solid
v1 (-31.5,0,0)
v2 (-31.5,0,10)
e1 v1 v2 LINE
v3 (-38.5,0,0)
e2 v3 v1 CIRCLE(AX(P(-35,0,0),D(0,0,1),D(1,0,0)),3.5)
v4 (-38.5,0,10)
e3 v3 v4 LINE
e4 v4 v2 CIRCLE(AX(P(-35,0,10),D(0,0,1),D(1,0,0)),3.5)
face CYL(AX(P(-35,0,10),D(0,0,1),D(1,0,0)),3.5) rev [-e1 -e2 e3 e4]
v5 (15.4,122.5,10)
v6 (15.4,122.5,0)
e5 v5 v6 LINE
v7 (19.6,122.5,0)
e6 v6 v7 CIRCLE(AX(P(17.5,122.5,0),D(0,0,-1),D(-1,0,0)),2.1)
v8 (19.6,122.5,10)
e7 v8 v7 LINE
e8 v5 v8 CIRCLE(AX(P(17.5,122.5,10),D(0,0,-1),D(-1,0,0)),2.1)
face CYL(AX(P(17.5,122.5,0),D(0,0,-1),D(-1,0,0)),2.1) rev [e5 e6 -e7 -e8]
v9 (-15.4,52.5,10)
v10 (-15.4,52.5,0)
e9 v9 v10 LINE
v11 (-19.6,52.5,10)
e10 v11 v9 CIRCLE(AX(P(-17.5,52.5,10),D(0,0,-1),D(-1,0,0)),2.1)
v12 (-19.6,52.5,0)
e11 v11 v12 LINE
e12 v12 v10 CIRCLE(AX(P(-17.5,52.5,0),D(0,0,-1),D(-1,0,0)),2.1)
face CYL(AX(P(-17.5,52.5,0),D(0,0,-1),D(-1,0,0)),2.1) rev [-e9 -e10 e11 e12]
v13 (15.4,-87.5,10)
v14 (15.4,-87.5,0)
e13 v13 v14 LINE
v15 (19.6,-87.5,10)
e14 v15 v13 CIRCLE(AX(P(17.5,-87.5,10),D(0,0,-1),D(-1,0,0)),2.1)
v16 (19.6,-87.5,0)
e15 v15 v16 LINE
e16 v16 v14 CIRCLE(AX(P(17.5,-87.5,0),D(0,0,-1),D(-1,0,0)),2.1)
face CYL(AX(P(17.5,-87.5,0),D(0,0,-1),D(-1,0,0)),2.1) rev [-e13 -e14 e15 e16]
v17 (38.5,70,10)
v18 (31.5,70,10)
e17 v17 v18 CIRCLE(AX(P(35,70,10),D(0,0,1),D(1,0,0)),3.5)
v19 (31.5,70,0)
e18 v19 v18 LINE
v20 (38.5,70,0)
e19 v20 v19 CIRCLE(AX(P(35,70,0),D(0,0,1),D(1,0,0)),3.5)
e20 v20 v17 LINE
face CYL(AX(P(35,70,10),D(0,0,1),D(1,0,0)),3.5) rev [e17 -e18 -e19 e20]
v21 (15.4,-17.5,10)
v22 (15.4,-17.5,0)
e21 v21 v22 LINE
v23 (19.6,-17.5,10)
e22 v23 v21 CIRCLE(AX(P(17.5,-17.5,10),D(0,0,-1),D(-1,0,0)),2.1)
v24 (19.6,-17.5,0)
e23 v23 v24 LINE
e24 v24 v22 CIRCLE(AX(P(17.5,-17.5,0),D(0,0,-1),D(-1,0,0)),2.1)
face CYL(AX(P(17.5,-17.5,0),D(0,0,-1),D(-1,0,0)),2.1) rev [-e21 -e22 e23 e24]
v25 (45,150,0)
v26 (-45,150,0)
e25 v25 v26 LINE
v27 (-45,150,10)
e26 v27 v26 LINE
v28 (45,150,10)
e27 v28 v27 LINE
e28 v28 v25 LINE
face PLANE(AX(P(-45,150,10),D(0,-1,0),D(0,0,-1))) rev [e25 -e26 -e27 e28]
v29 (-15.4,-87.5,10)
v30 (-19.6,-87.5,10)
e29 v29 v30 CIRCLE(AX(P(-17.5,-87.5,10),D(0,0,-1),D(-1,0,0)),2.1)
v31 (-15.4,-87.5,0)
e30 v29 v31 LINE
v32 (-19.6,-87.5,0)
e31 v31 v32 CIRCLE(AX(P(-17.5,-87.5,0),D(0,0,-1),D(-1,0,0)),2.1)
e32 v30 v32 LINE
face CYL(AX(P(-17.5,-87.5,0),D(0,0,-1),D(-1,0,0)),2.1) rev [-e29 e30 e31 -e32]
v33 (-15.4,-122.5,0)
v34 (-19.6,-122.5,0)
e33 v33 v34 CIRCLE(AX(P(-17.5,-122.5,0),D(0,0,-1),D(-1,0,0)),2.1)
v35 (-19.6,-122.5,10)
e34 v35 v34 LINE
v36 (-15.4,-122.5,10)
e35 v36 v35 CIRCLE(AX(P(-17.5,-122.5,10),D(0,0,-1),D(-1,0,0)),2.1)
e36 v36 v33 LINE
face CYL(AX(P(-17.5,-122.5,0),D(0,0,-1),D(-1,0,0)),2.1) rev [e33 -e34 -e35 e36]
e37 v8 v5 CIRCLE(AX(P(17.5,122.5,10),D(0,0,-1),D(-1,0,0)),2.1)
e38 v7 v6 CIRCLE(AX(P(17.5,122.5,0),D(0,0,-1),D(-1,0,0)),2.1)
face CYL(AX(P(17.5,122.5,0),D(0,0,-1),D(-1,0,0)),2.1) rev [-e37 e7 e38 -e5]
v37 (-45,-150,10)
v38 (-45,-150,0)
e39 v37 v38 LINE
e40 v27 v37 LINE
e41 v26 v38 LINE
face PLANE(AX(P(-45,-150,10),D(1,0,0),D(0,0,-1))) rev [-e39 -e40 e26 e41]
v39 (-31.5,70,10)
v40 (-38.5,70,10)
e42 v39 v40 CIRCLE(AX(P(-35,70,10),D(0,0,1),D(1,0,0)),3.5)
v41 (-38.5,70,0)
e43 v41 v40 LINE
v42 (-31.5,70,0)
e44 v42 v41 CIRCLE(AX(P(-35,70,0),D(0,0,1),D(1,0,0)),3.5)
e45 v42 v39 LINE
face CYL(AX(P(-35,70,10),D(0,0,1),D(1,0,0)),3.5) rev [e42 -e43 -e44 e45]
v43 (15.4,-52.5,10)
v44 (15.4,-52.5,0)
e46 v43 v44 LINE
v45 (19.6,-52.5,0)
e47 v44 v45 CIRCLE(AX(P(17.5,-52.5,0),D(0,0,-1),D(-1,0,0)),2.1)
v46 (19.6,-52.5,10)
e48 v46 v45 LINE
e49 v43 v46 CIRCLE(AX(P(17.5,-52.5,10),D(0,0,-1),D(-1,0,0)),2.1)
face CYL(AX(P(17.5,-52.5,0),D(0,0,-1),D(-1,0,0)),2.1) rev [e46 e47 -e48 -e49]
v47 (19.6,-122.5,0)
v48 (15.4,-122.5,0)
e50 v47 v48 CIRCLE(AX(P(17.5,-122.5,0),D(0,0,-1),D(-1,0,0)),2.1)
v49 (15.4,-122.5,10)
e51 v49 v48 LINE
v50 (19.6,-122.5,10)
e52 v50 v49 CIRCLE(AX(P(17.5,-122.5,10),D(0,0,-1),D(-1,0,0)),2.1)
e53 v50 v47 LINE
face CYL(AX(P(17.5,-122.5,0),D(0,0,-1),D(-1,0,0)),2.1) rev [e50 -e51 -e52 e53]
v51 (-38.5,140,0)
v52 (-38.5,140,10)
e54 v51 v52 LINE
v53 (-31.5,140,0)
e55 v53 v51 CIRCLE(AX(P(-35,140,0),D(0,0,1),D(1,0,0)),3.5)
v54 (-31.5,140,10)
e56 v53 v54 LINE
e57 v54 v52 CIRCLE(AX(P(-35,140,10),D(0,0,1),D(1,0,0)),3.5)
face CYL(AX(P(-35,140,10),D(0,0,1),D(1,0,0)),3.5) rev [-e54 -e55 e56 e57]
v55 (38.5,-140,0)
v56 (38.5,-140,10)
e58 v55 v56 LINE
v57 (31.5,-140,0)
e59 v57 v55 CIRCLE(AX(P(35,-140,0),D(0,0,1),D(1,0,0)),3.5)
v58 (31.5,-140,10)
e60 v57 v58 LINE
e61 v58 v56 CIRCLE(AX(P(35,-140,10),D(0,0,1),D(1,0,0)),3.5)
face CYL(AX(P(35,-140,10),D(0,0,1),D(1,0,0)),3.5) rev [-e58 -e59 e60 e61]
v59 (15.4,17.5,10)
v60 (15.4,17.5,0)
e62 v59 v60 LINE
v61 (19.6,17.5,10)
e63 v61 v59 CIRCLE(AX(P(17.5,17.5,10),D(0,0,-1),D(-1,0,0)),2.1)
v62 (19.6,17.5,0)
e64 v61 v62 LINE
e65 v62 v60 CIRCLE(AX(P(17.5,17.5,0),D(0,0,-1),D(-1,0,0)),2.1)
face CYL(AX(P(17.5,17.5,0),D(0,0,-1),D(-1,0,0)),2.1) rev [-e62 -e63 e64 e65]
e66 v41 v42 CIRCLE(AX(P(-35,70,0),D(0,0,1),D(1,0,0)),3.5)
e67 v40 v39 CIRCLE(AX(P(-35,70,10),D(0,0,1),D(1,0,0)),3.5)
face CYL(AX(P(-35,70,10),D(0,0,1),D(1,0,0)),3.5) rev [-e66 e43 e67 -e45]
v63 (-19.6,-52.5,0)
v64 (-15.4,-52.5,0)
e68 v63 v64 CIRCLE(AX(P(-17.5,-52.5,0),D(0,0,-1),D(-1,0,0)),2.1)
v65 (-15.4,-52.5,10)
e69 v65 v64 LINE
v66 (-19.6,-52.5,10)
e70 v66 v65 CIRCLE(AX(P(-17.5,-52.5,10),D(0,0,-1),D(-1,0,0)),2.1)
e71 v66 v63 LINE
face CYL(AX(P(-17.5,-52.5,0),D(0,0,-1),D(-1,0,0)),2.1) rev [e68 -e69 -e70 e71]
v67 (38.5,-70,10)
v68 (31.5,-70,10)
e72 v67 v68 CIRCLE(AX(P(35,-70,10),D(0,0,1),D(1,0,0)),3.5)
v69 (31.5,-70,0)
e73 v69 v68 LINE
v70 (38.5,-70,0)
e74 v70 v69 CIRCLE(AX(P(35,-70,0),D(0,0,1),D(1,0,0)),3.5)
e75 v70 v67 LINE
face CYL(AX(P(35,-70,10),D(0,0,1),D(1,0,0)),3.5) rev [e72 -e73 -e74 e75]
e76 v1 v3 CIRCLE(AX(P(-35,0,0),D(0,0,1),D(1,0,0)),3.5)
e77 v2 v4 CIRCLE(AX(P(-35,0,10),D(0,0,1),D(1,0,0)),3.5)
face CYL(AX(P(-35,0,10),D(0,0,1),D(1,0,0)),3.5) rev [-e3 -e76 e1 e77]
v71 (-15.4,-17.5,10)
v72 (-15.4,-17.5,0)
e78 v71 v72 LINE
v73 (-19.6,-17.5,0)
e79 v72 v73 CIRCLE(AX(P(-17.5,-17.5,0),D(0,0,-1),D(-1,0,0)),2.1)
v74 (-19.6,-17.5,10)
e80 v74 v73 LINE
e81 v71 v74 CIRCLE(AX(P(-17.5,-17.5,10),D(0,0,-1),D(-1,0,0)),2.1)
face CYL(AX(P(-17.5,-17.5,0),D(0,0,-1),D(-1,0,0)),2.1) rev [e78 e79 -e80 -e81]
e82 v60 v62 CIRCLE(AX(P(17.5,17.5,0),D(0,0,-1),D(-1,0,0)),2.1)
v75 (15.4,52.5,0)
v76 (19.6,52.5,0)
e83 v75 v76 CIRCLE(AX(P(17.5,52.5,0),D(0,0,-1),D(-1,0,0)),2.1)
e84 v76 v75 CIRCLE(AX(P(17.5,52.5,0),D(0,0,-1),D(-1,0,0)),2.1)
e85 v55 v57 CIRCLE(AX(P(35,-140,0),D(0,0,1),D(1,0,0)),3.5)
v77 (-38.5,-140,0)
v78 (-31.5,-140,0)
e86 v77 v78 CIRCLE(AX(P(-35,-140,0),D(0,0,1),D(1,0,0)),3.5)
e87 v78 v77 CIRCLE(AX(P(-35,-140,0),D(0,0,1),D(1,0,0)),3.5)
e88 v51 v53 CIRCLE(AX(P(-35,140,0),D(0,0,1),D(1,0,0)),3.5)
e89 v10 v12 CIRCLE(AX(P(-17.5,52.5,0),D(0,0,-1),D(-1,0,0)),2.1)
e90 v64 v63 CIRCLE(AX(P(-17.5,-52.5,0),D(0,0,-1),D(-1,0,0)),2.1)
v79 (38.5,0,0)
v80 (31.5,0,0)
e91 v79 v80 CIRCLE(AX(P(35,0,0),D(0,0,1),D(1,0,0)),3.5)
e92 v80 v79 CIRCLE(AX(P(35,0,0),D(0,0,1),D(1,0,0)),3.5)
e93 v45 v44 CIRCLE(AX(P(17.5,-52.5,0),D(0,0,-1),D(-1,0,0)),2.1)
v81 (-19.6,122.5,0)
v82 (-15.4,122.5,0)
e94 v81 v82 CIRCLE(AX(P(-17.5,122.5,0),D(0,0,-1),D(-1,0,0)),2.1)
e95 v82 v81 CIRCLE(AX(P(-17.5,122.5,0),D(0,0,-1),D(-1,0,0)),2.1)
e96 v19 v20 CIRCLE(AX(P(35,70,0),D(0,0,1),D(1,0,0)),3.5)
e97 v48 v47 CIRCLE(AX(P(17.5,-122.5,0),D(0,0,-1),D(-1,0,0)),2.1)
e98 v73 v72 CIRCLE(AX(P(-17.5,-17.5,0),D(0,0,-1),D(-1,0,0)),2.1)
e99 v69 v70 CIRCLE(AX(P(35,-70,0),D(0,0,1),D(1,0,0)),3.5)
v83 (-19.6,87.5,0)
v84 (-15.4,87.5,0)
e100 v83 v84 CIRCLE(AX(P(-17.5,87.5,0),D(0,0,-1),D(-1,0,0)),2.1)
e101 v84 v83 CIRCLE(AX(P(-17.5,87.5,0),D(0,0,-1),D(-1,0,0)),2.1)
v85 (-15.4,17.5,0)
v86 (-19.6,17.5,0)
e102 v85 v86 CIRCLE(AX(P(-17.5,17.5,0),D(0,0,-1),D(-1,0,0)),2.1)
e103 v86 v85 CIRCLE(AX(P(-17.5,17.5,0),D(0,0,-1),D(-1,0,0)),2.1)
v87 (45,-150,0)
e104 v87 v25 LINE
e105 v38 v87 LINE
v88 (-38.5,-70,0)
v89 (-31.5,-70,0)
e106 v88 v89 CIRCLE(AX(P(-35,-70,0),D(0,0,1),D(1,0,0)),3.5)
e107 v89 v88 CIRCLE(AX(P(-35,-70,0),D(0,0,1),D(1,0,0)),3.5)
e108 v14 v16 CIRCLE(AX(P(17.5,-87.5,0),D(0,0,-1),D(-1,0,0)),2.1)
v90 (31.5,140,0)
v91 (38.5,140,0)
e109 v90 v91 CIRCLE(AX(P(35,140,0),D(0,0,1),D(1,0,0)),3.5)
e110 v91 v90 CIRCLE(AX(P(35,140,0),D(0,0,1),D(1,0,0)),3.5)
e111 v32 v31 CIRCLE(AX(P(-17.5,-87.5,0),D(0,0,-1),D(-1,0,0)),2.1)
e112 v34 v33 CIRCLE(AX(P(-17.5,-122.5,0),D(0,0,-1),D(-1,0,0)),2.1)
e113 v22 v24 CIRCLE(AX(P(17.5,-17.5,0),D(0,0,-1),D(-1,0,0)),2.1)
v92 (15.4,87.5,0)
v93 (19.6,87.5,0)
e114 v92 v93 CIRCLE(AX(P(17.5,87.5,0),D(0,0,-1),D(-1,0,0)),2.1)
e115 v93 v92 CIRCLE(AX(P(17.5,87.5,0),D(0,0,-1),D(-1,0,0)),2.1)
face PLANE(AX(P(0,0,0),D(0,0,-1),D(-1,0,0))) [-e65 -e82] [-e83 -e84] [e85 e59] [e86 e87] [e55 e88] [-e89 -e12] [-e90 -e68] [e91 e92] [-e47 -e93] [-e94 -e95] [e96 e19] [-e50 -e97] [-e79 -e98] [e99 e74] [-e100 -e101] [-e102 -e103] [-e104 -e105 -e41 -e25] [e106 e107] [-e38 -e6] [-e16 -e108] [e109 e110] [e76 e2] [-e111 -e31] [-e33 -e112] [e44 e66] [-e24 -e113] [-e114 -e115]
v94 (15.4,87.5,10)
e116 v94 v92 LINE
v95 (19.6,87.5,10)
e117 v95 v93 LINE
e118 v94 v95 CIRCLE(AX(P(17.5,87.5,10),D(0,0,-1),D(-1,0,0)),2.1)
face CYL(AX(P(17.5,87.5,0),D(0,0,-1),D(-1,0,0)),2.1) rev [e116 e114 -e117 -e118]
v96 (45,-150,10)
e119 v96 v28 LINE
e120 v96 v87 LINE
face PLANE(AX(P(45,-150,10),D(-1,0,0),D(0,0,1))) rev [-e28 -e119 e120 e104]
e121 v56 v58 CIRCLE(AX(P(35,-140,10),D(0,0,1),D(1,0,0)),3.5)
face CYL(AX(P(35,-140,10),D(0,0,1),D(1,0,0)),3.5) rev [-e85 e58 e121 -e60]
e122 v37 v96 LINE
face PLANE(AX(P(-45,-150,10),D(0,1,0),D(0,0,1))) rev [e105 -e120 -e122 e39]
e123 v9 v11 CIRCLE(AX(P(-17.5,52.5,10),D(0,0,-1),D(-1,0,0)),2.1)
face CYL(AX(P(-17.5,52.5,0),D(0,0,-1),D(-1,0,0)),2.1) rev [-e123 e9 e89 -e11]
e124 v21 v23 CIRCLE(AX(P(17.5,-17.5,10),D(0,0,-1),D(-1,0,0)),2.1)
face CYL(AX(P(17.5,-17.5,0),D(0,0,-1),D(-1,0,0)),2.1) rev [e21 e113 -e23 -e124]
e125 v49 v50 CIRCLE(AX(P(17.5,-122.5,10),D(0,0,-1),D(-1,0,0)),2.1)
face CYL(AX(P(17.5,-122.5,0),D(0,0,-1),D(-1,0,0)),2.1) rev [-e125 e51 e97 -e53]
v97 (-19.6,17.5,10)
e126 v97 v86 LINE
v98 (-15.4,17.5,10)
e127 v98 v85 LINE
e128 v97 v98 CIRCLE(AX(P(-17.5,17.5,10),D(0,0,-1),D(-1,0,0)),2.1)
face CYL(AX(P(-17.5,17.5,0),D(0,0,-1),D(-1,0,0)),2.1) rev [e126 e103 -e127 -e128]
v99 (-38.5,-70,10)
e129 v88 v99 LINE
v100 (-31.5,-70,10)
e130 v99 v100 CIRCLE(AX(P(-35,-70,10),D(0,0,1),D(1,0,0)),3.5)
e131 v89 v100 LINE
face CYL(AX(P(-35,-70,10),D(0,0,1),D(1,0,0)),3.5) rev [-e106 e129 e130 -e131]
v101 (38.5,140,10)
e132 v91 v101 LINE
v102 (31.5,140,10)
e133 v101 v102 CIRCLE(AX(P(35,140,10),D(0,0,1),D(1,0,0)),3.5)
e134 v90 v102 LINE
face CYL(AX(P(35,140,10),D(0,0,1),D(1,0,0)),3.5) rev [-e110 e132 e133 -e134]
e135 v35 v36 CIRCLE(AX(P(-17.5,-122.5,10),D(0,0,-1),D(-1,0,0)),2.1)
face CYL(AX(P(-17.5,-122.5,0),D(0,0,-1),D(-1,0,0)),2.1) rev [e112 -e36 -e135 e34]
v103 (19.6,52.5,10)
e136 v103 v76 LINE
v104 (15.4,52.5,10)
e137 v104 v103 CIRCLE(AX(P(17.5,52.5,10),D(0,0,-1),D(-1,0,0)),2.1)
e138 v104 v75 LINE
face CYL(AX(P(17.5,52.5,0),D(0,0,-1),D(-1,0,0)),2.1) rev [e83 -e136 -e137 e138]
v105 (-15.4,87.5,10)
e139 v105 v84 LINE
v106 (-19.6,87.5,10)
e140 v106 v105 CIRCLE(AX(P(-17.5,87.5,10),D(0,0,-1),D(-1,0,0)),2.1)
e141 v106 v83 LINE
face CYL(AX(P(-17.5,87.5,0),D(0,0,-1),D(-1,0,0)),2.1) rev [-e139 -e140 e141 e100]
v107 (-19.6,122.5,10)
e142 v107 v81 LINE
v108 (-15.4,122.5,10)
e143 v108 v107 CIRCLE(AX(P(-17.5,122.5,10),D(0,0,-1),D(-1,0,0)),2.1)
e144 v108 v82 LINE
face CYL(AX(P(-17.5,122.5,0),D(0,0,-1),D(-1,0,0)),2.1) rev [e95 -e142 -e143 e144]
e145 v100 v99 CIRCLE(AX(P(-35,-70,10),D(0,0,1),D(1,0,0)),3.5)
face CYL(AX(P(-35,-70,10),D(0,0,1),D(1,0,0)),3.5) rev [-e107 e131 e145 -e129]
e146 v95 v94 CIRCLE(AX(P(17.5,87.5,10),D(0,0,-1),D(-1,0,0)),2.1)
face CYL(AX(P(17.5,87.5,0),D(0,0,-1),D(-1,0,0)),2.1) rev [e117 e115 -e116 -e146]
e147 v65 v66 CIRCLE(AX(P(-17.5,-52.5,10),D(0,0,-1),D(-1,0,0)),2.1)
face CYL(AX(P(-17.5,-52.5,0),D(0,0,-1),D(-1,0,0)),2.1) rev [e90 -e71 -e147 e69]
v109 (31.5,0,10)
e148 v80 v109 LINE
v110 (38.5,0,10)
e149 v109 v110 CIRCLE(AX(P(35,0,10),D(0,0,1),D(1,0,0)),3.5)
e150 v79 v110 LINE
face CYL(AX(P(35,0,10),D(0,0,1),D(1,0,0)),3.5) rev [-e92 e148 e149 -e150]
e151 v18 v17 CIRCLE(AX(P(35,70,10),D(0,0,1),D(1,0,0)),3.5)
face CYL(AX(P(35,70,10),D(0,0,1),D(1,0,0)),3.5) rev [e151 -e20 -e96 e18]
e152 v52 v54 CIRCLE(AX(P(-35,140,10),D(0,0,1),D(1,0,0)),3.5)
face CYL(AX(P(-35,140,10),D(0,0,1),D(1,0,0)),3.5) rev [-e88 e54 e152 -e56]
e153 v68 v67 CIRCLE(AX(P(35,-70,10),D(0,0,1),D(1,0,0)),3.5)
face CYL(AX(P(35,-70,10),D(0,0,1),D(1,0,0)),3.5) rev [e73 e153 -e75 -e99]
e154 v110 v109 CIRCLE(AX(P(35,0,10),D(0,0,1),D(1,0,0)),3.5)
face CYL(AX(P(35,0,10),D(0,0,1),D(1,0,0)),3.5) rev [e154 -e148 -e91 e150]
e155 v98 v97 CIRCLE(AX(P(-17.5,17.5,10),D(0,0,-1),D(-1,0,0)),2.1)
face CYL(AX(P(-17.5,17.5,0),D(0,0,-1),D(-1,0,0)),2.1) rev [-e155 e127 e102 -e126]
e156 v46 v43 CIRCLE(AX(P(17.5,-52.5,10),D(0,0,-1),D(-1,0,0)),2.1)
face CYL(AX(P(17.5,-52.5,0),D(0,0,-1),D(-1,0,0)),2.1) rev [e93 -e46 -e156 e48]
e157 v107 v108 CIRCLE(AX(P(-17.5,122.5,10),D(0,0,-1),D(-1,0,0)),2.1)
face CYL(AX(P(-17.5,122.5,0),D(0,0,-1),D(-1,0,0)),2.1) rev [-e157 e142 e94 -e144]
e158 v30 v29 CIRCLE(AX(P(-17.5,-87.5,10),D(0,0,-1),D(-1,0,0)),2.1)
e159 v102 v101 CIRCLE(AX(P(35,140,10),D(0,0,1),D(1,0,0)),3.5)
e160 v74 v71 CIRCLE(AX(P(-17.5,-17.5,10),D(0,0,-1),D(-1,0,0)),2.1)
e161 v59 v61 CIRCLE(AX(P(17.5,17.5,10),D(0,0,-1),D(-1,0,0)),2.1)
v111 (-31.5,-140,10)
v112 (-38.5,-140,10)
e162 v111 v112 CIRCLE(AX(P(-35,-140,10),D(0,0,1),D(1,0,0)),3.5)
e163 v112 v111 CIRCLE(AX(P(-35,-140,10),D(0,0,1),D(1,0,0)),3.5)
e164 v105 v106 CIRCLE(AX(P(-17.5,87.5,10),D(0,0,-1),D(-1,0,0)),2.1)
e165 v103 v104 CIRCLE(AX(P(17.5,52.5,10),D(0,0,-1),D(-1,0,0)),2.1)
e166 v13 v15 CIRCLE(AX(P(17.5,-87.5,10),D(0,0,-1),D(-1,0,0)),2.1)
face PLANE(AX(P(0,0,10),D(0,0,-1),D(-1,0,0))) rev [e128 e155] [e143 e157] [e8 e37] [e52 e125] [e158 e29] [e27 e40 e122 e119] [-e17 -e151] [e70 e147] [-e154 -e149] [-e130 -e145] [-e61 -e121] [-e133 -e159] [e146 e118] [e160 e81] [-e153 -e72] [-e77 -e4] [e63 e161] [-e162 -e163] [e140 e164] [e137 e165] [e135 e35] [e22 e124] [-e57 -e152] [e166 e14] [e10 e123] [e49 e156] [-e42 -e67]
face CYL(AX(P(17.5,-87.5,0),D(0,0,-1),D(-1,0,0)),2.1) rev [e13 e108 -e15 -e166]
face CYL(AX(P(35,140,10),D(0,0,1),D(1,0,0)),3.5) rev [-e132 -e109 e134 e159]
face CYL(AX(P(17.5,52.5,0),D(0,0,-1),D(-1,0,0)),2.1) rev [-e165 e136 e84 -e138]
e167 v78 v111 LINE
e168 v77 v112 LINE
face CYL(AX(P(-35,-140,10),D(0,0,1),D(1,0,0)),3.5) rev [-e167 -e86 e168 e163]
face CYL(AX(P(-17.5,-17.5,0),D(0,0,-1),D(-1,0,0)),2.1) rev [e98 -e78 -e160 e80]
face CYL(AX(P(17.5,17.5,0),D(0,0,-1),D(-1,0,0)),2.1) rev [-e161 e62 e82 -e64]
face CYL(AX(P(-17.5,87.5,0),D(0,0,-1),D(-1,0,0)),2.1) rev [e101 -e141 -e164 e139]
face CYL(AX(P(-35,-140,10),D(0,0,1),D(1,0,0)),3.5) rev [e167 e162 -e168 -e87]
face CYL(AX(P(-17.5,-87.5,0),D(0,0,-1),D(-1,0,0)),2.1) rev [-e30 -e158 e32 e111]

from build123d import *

# Parameters (mm, degrees)
SKETCH1_W                = 90
SKETCH1_H                = 300
BOSS_EXTRUDE1_DEPTH      = 10
F_7_0_7_DIAMETER_HOLE1_D = 7
LPATTERN1_COUNT          = 3
LPATTERN1_PITCH          = 70
LPATTERN1_COUNT_DIR2     = 2
LPATTERN1_PITCH_DIR2     = 70
LPATTERN2_COUNT          = 3
LPATTERN2_PITCH          = 70
LPATTERN2_COPY_1_D       = 7
LPATTERN2_COPY_2_D       = 7
LPATTERN2_COPY_3_D       = 7
LPATTERN2_COPY_4_D       = 7
LPATTERN2_COPY_5_D       = 7
LPATTERN2_COPY_6_D       = 7
LPATTERN2_COPY_7_D       = 7
LPATTERN2_COPY_8_D       = 7
LPATTERN2_COPY_9_D       = 7
LPATTERN2_COPY_10_D      = 7
M5_TAPPED_HOLE1_D        = 4.2
LPATTERN3_COUNT          = 4
LPATTERN3_PITCH          = 35
LPATTERN3_COL_COUNT      = 4
LPATTERN3_COL_PITCH      = 35


with BuildPart() as part:
    # Sketch1 → Boss-Extrude1 (new body)
    with BuildSketch(Plane.XY):
        Rectangle(SKETCH1_W, SKETCH1_H)
    extrude(amount=BOSS_EXTRUDE1_DEPTH)

    # Ø7.0 (7) Diameter Hole1 (through all)
    with Locations(Plane.XY.offset(10)):
        with Locations((-35, 0)):
            f_7_0_7_diameter_hole1 = Hole(F_7_0_7_DIAMETER_HOLE1_D / 2)

    # LPattern1: 7.0 _7_ Diameter Hole1 3 × 2
    with Locations(*[(j * LPATTERN1_PITCH_DIR2, -i * LPATTERN1_PITCH, 0) for i in range(LPATTERN1_COUNT) for j in range(LPATTERN1_COUNT_DIR2) if (i, j) != (0, 0)]):
        add(f_7_0_7_diameter_hole1, mode=Mode.SUBTRACT)

    # LPattern2: Ø7.0 (7) Diameter Hole1 ×3
    with Locations(*[(0, i * LPATTERN2_PITCH, 0) for i in range(1, LPATTERN2_COUNT)]):
        add(f_7_0_7_diameter_hole1, mode=Mode.SUBTRACT)

    # LPattern2 copy 1 (through all)
    with Locations(Plane(origin=(70, 70, 10), x_dir=(1, 0, 0), z_dir=(0, 0, 1))):
        with Locations((-35, 0)):
            Hole(LPATTERN2_COPY_1_D / 2)

    # LPattern2 copy 2 (through all)
    with Locations(Plane(origin=(70, 140, 10), x_dir=(1, 0, 0), z_dir=(0, 0, 1))):
        with Locations((-35, 0)):
            Hole(LPATTERN2_COPY_2_D / 2)

    # LPattern2 copy 3 (through all)
    with Locations(Plane.XY.offset(10)):
        with Locations((-35, 0)):
            Hole(LPATTERN2_COPY_3_D / 2)

    # LPattern2 copy 4 (through all)
    with Locations(Plane(origin=(0, 70, 10), x_dir=(1, 0, 0), z_dir=(0, 0, 1))):
        with Locations((-35, 0)):
            Hole(LPATTERN2_COPY_4_D / 2)

    # LPattern2 copy 5 (through all)
    with Locations(Plane(origin=(70, 0, 10), x_dir=(1, 0, 0), z_dir=(0, 0, 1))):
        with Locations((-35, 0)):
            Hole(LPATTERN2_COPY_5_D / 2)

    # LPattern2 copy 6 (through all)
    with Locations(Plane(origin=(70, 70, 10), x_dir=(1, 0, 0), z_dir=(0, 0, 1))):
        with Locations((-35, 0)):
            Hole(LPATTERN2_COPY_6_D / 2)

    # LPattern2 copy 7 (through all)
    with Locations(Plane(origin=(0, -70, 10), x_dir=(1, 0, 0), z_dir=(0, 0, 1))):
        with Locations((-35, 0)):
            Hole(LPATTERN2_COPY_7_D / 2)

    # LPattern2 copy 8 (through all)
    with Locations(Plane.XY.offset(10)):
        with Locations((-35, 0)):
            Hole(LPATTERN2_COPY_8_D / 2)

    # LPattern2 copy 9 (through all)
    with Locations(Plane(origin=(70, -70, 10), x_dir=(1, 0, 0), z_dir=(0, 0, 1))):
        with Locations((-35, 0)):
            Hole(LPATTERN2_COPY_9_D / 2)

    # LPattern2 copy 10 (through all)
    with Locations(Plane(origin=(70, 0, 10), x_dir=(1, 0, 0), z_dir=(0, 0, 1))):
        with Locations((-35, 0)):
            Hole(LPATTERN2_COPY_10_D / 2)

    # M5 Tapped Hole1 (through all)
    with Locations(Plane(origin=(0, 0, 0), x_dir=(-1, 0, 0), z_dir=(0, 0, -1))):
        with Locations((17.5, 17.5), (17.5, -17.5), (-17.5, -17.5), (-17.5, 17.5)):
            m5_tapped_hole1 = Hole(M5_TAPPED_HOLE1_D / 2)

    # LPattern3: M5 Tapped Hole1 ×4
    with Locations(*[(0, -i * LPATTERN3_PITCH, 0) for i in range(1, LPATTERN3_COUNT)]):
        add(m5_tapped_hole1, mode=Mode.SUBTRACT)

    # LPattern3 col: M5 Tapped Hole1 ×4
    with Locations(*[(0, i * LPATTERN3_COL_PITCH, 0) for i in range(1, LPATTERN3_COL_COUNT)]):
        add(m5_tapped_hole1, mode=Mode.SUBTRACT)


solid = part.part
